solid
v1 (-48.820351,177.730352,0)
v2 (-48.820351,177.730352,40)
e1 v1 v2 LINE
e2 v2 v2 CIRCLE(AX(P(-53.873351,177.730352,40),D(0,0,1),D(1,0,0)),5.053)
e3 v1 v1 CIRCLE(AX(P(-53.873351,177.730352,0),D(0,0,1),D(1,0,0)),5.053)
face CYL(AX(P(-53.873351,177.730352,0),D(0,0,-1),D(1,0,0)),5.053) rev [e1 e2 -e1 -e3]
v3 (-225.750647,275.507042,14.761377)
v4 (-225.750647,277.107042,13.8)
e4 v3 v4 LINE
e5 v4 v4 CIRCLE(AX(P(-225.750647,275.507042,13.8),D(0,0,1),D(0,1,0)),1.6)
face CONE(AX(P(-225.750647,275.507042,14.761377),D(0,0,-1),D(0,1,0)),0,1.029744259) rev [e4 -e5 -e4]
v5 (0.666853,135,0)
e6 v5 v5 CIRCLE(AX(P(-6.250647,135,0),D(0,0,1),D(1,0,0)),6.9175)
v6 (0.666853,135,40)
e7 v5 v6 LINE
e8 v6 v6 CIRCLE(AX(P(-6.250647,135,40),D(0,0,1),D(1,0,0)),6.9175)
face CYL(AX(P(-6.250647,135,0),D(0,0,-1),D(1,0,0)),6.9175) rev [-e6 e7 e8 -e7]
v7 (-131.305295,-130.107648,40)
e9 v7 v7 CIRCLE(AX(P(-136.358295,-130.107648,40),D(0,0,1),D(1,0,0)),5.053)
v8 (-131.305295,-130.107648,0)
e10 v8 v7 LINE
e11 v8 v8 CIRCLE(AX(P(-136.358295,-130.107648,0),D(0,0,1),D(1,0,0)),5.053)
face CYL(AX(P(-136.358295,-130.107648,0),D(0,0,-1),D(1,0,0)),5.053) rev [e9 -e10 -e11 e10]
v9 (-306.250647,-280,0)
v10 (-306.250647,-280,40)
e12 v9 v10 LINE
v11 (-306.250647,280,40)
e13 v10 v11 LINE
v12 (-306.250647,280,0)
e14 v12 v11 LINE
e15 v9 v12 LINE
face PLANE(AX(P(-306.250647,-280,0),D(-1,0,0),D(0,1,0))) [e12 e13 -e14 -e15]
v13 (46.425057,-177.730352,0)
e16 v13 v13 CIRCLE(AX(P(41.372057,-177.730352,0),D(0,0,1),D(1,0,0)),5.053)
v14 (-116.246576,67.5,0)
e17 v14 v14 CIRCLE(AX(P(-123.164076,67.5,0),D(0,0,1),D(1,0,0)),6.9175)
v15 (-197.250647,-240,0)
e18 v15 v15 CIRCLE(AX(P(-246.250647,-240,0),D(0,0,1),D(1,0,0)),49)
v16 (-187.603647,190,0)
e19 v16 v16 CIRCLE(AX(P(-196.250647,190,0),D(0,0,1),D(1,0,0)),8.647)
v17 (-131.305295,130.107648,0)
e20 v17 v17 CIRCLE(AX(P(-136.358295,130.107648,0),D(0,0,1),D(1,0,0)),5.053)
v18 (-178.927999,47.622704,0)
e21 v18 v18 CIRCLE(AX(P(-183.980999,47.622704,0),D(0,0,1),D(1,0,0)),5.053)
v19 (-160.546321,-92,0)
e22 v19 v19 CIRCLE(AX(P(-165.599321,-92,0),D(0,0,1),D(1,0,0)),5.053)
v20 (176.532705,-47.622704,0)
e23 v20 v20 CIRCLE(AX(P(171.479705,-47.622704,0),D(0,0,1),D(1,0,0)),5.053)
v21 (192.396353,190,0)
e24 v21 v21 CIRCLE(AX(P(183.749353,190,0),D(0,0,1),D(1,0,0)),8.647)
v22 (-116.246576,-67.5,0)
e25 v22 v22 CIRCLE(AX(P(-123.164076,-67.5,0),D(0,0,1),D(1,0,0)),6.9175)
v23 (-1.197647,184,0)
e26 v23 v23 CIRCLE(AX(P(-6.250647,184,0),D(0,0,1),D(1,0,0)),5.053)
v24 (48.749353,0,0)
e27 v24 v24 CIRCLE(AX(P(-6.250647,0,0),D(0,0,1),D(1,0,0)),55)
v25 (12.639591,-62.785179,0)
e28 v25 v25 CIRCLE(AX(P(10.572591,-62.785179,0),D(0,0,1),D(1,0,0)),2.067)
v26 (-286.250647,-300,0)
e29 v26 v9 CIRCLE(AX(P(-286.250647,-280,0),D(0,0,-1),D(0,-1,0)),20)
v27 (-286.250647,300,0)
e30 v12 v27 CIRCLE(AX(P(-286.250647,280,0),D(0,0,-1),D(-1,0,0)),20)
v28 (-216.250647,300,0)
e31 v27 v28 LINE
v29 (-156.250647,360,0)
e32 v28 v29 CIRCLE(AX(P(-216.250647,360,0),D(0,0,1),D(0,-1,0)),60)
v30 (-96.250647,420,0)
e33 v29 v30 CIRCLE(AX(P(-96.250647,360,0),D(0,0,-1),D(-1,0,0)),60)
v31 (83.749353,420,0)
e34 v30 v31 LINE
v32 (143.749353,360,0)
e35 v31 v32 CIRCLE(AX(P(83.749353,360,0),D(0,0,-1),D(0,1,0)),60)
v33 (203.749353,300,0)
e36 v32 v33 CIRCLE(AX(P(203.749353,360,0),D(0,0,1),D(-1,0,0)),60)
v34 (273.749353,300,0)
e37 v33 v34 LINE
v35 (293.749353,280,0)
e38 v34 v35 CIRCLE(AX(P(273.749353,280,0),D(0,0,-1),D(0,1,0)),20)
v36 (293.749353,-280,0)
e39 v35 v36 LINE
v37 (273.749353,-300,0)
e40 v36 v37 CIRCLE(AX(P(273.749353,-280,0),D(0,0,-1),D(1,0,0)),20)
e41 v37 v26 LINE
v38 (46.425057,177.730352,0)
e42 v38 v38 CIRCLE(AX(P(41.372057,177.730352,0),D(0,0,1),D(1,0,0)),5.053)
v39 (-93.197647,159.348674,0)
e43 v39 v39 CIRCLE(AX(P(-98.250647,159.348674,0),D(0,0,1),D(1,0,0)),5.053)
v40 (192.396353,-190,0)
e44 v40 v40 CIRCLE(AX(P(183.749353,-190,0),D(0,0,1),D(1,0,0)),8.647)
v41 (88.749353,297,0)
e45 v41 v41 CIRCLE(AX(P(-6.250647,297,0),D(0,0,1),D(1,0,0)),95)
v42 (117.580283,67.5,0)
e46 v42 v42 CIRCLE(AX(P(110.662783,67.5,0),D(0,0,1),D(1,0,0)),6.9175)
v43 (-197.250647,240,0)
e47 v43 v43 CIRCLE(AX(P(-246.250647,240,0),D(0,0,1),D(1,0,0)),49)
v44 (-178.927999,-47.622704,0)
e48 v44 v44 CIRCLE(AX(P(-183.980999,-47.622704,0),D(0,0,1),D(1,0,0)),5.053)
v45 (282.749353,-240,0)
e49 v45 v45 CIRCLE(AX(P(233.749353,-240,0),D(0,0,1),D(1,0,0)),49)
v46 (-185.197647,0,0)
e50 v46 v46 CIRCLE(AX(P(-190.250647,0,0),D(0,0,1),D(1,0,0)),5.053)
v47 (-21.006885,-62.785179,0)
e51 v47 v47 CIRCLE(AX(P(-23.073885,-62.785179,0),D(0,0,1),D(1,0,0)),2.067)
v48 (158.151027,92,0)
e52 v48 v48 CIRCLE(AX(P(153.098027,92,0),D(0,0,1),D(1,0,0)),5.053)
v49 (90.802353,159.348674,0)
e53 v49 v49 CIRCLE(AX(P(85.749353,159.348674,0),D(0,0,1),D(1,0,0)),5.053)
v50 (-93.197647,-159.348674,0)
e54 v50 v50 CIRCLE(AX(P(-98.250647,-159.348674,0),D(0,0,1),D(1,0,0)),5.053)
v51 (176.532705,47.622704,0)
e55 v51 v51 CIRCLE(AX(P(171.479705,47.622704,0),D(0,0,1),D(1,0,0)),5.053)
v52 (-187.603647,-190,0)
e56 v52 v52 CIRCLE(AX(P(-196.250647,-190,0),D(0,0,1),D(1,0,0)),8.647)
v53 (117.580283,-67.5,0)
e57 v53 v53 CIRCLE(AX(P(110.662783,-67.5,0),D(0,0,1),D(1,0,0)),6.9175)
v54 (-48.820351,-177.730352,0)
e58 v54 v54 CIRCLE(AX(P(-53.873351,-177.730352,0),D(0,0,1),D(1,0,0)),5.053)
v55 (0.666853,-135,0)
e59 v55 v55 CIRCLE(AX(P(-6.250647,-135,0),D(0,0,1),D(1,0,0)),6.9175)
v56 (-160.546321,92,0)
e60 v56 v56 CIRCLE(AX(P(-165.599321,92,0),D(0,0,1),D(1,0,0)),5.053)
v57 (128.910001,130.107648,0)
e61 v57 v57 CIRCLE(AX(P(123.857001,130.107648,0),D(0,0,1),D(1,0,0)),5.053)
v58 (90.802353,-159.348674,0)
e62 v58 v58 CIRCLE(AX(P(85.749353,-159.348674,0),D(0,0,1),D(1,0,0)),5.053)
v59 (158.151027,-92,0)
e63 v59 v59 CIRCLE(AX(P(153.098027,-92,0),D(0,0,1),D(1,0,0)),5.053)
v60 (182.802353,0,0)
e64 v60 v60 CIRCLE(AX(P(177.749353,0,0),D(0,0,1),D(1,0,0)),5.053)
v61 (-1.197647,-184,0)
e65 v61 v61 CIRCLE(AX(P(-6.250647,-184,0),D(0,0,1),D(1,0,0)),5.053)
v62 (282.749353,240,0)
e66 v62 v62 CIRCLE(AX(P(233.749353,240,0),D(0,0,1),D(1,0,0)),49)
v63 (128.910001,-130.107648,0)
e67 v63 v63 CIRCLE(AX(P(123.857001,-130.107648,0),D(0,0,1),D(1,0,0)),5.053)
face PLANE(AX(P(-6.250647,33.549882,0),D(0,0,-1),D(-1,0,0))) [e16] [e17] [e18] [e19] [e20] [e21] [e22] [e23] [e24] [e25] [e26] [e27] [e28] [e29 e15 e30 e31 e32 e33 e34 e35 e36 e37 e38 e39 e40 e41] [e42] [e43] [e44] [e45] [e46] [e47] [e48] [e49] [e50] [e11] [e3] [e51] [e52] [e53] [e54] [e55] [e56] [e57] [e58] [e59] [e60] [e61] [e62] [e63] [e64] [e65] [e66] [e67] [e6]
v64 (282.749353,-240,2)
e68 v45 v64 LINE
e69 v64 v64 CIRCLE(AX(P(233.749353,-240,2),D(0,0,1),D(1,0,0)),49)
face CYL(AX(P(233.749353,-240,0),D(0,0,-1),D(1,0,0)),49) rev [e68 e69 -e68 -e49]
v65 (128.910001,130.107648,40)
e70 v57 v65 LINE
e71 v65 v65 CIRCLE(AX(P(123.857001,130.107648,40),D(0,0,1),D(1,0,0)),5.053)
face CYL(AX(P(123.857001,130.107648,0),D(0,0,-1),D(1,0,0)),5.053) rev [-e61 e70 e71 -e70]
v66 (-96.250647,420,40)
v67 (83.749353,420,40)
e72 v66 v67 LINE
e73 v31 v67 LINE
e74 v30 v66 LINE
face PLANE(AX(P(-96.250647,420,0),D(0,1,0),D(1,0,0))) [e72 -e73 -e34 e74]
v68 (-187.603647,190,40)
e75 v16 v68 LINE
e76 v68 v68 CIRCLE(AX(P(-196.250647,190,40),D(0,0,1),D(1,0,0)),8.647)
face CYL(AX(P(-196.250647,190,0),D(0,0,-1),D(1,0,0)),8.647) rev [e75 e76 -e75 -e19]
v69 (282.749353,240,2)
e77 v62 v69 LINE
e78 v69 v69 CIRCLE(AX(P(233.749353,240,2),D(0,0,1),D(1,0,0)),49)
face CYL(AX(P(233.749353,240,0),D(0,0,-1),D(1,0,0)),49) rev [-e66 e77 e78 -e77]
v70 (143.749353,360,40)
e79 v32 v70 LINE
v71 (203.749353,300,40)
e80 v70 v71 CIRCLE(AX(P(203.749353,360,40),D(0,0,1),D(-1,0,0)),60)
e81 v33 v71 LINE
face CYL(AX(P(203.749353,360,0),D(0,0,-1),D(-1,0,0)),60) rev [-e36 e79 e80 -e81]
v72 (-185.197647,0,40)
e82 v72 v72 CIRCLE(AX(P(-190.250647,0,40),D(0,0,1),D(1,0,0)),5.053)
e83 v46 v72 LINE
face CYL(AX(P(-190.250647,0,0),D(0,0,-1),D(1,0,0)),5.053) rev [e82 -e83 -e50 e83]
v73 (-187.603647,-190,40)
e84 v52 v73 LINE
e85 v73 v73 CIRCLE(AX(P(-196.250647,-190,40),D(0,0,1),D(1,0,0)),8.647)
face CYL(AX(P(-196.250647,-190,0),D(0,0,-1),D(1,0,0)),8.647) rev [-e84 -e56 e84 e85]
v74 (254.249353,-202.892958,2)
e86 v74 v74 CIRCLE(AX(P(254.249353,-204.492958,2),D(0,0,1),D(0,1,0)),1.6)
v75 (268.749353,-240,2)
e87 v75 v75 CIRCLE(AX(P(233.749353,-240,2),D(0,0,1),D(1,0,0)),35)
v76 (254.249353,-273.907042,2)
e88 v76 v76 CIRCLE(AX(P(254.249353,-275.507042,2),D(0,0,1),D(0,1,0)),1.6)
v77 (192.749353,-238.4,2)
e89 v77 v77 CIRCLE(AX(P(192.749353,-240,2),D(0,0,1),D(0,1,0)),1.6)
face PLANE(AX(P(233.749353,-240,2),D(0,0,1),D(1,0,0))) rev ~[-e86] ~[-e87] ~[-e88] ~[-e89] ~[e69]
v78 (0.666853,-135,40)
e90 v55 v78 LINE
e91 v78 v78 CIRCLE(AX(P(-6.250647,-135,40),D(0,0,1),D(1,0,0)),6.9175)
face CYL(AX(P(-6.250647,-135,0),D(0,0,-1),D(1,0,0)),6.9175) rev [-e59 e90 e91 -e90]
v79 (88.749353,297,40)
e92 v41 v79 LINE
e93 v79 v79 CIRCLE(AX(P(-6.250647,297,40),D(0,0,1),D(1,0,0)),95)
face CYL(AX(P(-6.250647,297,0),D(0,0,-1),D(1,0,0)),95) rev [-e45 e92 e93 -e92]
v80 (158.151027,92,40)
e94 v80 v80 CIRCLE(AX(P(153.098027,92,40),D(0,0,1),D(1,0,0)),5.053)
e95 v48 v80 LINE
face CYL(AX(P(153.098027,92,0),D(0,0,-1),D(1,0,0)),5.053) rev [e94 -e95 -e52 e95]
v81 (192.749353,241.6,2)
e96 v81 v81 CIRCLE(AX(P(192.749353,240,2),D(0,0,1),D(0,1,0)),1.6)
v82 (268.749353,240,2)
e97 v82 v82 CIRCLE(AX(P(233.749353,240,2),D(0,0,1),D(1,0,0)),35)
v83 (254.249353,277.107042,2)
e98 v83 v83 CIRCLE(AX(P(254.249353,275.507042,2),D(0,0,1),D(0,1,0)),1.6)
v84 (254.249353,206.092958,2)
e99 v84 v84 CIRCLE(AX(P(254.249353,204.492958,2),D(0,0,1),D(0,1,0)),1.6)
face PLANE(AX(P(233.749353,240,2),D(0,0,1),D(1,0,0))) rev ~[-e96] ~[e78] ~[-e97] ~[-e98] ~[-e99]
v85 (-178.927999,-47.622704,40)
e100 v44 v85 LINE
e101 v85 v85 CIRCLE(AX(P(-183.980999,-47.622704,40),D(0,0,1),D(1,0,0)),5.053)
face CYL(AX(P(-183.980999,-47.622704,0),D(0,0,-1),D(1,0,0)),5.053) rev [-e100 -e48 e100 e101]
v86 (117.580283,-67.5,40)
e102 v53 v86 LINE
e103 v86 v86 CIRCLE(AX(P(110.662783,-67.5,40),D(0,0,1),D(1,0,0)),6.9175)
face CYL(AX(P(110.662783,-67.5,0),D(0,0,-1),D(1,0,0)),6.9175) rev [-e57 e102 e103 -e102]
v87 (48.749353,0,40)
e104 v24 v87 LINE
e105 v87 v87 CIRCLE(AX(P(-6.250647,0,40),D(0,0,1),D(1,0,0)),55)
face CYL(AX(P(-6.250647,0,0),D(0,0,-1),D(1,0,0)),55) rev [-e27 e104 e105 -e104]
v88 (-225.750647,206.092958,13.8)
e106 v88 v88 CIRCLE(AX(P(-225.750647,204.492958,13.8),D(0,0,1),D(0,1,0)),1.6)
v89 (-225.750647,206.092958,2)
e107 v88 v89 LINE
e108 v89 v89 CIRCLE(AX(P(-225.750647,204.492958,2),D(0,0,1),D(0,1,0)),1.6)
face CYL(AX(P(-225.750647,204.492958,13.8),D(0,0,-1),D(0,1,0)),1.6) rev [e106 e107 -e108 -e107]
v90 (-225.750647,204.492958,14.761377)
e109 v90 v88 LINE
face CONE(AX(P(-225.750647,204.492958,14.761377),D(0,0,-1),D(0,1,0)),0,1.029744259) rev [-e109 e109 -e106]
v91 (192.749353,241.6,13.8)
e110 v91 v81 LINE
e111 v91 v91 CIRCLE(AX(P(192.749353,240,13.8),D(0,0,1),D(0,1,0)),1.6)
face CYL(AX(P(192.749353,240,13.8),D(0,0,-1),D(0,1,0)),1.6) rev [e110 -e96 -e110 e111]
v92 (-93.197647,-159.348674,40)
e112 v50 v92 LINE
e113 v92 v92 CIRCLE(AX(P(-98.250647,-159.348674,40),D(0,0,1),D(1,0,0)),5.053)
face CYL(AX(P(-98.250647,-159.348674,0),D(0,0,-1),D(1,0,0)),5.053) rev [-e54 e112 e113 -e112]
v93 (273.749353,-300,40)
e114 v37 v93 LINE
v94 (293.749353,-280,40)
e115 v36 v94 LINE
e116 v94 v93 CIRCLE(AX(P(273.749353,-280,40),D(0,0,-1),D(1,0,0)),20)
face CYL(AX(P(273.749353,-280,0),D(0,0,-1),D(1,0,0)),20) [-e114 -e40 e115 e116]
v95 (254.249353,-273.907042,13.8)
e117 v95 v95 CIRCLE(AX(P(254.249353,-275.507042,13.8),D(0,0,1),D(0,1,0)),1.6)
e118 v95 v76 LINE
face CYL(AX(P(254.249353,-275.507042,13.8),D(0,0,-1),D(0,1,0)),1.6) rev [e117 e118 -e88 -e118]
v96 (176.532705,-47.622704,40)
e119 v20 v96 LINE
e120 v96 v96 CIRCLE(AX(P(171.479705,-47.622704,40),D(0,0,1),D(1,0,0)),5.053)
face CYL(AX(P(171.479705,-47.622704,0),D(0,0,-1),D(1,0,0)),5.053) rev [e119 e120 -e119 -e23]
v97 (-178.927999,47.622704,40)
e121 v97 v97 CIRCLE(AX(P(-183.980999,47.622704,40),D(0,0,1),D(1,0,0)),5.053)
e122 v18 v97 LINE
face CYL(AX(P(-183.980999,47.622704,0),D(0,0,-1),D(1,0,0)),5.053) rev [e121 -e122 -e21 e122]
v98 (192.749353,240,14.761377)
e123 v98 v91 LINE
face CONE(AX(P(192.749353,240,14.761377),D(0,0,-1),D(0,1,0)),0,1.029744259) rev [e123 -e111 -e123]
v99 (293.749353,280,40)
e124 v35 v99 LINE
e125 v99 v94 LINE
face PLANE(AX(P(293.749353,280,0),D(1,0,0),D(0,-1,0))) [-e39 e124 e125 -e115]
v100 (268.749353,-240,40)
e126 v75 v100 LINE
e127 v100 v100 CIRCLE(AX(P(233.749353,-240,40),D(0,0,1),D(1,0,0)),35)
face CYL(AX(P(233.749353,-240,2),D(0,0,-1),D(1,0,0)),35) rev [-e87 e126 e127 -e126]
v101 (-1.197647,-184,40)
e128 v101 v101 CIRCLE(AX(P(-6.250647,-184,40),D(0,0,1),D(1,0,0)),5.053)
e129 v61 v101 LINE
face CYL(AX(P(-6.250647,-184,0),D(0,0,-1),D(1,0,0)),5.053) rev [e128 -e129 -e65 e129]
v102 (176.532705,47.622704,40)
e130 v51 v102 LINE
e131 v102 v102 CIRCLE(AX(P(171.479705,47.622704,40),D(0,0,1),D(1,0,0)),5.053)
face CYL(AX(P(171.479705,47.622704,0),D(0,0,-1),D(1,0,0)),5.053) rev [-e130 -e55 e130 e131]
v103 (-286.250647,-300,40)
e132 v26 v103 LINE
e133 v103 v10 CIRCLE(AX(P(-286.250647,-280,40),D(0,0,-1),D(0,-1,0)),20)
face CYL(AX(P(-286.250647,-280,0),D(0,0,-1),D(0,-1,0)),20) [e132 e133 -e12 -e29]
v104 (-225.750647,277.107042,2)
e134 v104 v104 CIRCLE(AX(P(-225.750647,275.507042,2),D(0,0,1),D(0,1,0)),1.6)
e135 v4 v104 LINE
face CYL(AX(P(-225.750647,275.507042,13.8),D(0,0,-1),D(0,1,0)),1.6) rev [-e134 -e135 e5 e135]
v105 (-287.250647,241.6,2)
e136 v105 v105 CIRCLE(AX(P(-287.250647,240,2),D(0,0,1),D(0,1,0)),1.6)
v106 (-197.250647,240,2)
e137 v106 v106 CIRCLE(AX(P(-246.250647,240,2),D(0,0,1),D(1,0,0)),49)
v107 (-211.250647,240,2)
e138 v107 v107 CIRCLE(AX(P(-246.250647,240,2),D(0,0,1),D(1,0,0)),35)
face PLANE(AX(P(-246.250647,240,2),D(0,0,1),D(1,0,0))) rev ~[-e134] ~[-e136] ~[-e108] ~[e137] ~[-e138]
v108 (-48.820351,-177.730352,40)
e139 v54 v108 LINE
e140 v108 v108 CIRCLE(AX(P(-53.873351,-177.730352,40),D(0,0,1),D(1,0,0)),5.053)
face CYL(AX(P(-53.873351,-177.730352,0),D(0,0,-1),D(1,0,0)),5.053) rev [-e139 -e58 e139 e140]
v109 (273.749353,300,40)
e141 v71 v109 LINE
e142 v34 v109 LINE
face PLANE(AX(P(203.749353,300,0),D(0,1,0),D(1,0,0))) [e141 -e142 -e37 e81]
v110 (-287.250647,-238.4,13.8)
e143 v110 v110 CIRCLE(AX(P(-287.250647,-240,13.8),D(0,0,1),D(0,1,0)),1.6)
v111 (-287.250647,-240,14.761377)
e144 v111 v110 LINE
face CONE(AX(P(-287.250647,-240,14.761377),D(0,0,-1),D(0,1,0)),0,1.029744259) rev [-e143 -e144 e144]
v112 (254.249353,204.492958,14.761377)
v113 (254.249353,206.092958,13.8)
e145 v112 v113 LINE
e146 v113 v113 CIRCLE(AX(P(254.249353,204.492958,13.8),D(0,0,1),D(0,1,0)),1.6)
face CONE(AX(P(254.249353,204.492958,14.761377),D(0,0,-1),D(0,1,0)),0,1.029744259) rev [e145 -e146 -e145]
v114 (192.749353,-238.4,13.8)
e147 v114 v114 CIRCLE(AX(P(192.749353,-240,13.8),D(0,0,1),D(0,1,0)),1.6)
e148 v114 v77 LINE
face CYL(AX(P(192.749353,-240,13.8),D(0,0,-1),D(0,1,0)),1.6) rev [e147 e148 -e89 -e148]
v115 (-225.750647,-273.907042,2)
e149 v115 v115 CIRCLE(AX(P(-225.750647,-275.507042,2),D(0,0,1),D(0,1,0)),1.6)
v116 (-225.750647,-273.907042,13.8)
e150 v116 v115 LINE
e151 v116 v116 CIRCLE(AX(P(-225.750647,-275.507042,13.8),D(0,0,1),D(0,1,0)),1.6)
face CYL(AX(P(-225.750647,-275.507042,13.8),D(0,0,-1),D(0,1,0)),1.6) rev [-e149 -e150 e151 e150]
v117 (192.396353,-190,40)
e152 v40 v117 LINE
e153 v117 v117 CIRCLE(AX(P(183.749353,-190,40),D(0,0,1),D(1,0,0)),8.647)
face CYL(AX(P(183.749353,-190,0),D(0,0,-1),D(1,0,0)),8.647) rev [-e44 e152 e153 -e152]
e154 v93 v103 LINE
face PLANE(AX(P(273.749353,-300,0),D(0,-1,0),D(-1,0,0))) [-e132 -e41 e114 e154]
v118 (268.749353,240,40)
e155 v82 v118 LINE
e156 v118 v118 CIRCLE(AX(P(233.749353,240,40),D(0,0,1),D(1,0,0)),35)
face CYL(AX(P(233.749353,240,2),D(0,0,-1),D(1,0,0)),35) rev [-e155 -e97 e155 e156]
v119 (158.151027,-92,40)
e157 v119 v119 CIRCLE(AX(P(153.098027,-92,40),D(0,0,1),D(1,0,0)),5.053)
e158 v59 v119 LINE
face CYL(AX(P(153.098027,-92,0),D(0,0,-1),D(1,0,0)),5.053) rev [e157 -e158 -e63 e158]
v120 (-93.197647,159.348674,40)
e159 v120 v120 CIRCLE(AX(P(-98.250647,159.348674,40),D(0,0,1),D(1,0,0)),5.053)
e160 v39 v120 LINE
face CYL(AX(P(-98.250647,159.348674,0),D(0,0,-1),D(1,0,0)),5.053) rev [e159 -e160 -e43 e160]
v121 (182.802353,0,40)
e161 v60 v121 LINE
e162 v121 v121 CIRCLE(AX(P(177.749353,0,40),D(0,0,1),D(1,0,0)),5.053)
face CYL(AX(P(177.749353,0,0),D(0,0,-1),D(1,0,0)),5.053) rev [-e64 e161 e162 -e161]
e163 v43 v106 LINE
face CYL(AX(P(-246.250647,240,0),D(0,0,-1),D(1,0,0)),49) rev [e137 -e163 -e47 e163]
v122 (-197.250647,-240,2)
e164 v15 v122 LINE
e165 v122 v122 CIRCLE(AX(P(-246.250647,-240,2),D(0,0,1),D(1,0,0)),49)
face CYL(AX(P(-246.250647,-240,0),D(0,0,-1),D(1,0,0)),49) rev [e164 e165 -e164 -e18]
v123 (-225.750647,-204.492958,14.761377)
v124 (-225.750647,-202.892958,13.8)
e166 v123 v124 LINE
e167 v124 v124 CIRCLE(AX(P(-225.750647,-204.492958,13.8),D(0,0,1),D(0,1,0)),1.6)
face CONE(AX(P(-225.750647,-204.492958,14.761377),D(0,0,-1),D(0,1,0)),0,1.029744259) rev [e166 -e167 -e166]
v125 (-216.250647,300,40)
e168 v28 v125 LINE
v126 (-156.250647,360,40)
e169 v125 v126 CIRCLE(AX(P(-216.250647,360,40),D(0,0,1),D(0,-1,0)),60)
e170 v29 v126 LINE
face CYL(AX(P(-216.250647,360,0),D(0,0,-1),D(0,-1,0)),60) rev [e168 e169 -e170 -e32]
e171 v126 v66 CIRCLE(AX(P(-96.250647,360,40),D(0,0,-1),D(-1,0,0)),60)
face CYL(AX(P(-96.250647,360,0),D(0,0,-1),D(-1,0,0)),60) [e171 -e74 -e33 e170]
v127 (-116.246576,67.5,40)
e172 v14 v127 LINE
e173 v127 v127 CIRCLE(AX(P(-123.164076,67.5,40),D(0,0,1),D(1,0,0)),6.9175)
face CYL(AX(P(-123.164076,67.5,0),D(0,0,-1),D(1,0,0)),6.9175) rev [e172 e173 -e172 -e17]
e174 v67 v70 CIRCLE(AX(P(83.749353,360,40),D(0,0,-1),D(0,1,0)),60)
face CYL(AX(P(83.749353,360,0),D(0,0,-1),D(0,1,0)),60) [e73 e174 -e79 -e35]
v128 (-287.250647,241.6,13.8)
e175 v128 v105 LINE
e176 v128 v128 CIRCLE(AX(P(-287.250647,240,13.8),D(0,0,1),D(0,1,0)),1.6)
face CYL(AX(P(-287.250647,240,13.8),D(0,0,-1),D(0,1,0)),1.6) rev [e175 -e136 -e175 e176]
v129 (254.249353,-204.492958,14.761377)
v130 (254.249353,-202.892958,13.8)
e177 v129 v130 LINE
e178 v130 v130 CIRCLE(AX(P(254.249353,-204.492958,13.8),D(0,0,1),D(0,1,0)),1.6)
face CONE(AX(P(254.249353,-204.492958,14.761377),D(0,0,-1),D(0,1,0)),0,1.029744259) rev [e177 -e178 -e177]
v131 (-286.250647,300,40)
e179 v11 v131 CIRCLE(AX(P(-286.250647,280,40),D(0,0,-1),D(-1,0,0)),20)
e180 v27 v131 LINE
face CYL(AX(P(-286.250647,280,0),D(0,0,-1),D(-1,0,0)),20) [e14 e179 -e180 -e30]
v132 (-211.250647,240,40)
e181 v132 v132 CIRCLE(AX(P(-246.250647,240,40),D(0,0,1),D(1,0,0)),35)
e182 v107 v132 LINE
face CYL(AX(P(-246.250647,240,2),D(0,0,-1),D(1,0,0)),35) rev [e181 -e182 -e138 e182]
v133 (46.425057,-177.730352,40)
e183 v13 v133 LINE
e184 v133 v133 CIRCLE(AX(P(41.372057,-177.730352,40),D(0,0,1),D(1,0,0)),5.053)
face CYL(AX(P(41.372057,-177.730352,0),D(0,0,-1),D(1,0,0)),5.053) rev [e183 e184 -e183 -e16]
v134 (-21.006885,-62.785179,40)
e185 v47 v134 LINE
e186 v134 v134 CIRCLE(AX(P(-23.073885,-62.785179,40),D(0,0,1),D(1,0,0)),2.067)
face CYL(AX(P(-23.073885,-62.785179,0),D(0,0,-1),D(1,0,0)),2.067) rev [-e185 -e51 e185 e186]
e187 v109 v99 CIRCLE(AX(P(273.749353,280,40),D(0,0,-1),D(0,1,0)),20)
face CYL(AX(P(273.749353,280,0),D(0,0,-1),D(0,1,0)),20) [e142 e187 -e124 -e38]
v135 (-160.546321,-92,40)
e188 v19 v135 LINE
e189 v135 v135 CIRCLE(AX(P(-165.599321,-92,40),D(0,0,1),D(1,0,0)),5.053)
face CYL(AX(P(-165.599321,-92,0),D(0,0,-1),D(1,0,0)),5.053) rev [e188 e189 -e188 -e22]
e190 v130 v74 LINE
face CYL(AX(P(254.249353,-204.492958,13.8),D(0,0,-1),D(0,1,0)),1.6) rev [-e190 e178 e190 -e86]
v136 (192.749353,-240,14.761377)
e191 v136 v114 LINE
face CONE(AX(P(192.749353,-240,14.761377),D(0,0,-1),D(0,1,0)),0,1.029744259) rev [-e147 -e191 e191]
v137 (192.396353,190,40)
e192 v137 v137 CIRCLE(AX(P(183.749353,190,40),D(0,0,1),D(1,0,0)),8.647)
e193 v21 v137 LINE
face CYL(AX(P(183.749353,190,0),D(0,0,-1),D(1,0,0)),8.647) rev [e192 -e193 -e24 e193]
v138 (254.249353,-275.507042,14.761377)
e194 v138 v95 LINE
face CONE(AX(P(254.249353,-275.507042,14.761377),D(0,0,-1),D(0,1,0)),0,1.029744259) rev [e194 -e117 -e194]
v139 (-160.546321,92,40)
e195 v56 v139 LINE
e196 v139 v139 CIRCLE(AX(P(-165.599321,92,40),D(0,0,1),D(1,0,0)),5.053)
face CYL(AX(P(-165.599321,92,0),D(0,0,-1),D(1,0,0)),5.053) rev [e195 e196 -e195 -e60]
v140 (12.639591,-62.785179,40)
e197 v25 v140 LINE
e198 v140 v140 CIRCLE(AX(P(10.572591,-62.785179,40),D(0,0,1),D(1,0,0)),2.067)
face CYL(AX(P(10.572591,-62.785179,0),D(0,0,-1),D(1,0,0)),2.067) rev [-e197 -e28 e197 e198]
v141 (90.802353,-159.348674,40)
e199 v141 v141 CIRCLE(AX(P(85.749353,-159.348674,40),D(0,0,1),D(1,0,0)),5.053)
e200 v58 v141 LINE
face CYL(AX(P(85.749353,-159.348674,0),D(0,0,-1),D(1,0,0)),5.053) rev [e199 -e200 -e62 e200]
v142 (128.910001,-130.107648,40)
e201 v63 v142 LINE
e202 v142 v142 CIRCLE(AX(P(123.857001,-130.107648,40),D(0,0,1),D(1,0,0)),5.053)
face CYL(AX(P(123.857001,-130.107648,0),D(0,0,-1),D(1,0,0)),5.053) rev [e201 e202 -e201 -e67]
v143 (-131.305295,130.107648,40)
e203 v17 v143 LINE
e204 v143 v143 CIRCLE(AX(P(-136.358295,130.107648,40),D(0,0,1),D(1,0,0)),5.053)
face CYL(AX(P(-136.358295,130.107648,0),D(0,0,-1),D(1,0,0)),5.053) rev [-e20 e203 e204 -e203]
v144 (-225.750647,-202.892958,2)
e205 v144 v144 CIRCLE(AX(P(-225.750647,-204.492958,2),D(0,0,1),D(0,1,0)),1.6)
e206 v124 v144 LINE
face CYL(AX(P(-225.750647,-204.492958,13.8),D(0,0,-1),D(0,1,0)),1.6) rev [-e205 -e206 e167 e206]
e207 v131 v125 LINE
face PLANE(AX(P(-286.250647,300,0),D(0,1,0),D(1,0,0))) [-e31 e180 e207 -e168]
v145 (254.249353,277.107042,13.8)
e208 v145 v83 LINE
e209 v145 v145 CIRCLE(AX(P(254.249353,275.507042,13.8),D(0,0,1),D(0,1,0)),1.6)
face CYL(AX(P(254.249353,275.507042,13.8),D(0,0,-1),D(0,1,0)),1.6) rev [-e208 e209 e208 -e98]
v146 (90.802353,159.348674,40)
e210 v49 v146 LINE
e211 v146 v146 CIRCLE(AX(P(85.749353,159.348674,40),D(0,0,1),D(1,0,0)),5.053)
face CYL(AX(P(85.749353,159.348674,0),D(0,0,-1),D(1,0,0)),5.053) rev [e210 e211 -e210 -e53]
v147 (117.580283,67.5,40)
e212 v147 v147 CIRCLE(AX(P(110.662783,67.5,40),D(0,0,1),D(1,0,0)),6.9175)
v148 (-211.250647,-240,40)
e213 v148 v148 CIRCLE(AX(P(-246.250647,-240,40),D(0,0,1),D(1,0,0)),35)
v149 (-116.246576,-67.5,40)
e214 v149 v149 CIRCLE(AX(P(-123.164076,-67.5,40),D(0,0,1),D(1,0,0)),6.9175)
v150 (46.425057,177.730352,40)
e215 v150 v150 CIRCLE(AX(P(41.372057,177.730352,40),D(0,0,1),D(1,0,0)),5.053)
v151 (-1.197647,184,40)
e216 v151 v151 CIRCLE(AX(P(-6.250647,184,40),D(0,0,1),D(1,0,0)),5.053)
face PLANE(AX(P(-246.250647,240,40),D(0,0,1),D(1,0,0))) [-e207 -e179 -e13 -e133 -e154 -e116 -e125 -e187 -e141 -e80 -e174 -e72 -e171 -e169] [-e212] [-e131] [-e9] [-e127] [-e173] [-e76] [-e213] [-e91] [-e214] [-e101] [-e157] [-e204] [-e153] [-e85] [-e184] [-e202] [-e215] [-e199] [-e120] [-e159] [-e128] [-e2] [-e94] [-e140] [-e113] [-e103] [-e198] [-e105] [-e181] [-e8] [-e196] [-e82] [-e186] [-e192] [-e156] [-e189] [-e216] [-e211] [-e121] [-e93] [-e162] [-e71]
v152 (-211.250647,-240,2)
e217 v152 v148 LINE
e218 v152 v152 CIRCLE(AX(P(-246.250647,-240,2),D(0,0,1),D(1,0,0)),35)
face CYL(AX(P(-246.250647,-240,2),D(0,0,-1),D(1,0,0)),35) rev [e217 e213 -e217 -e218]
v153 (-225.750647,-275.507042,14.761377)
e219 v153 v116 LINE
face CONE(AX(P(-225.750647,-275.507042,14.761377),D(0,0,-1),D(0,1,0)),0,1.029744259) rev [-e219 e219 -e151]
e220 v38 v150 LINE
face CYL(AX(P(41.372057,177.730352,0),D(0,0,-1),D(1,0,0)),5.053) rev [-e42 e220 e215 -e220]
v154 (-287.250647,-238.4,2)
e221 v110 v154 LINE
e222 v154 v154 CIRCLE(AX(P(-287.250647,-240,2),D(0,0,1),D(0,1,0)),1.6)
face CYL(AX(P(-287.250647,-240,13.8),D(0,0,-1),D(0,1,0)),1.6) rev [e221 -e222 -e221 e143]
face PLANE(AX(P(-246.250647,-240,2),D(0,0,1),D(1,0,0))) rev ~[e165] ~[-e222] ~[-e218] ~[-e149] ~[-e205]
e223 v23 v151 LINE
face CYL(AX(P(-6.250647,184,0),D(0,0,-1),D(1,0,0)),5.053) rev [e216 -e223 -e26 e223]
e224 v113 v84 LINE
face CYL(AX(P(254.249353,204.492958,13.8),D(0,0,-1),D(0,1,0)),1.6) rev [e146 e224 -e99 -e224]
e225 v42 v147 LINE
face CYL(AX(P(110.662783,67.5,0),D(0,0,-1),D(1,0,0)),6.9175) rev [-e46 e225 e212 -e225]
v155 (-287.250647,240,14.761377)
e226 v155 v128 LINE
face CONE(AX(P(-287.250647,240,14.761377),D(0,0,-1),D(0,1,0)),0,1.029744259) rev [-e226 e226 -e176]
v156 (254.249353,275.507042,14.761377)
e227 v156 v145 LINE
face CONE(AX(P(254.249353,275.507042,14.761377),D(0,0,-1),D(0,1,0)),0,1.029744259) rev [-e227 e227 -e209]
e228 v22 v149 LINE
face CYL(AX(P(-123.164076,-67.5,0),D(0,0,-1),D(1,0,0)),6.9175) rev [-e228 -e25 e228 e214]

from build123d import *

# Parameters (mm, degrees)
SKETCH1_R                       = 49
SKETCH1_R_2                     = 55
SKETCH1_R_3                     = 5.053
SKETCH1_R_4                     = 95
SKETCH1_R_5                     = 6.9175
SKETCH1_R_6                     = 8.647
SKETCH1_R_7                     = 2.067
BOSS_EXTRUDE1_DEPTH             = 40
BOSS_EXTRUDE2_START             = -38
SKETCH2_R                       = 49
SKETCH2_R_2                     = 35
BOSS_EXTRUDE2_DEPTH             = 38
SIZE_MM_DOWEL_HOLE_1_AT_2_COUNT = 2
SIZE_MM_DOWEL_HOLE_1_AT_2_PITCH = 71.01408311
SIZE_MM_DOWEL_HOLE_1_AT_3_COUNT = 2
SIZE_MM_DOWEL_HOLE_1_AT_3_PITCH = 71.01408311
LPATTERN1_COUNT                 = 2
LPATTERN1_PITCH                 = 480
LPATTERN1_COUNT_DIR2            = 2
LPATTERN1_PITCH_DIR2            = 480


with BuildPart() as part:
    # Sketch1 → Boss-Extrude1 (new body)
    with BuildSketch(Plane.XY):
        with BuildLine():
            Line((-96.250646967, 420), (83.749353033, 420))
            ThreePointArc((83.749353033, 420), (126.175759905, 402.426406871), (143.749353033, 360))
            ThreePointArc((143.749353033, 360), (161.322946162, 317.573593129), (203.749353033, 300))
            Line((203.749353033, 300), (273.749353033, 300))
            ThreePointArc((273.749353033, 300), (287.891488657, 294.142135624), (293.749353033, 280))
            Line((293.749353033, 280), (293.749353033, -280))
            ThreePointArc((293.749353033, -280), (287.891488657, -294.142135624), (273.749353033, -300))
            Line((273.749353033, -300), (-286.250646967, -300))
            ThreePointArc((-286.250646967, -300), (-300.39278259, -294.142135624), (-306.250646967, -280))
            Line((-306.250646967, -280), (-306.250646967, 280))
            ThreePointArc((-306.250646967, 280), (-300.39278259, 294.142135624), (-286.250646967, 300))
            Line((-286.250646967, 300), (-216.250646967, 300))
            ThreePointArc((-216.250646967, 300), (-173.824240095, 317.573593129), (-156.250646967, 360))
            ThreePointArc((-156.250646967, 360), (-138.677053838, 402.426406871), (-96.250646967, 420))
        make_face()
        with Locations((-246.250646967, 240)):
            Circle(SKETCH1_R, mode=Mode.SUBTRACT)
        with Locations((233.749353033, -240)):
            Circle(SKETCH1_R, mode=Mode.SUBTRACT)
        with Locations((-246.250646967, -240)):
            Circle(SKETCH1_R, mode=Mode.SUBTRACT)
        with Locations((233.749353033, 240)):
            Circle(SKETCH1_R, mode=Mode.SUBTRACT)
        with Locations((-6.250646967, 0)):
            Circle(SKETCH1_R_2, mode=Mode.SUBTRACT)
        with Locations((-6.250646967, -184)):
            Circle(SKETCH1_R_3, mode=Mode.SUBTRACT)
        with Locations((-53.873351265, -177.730352037)):
            Circle(SKETCH1_R_3, mode=Mode.SUBTRACT)
        with Locations((-98.250646967, -159.348674296)):
            Circle(SKETCH1_R_3, mode=Mode.SUBTRACT)
        with Locations((-136.358294705, -130.107647738)):
            Circle(SKETCH1_R_3, mode=Mode.SUBTRACT)
        with Locations((-165.599321263, -92)):
            Circle(SKETCH1_R_3, mode=Mode.SUBTRACT)
        with Locations((-183.980999004, -47.622704299)):
            Circle(SKETCH1_R_3, mode=Mode.SUBTRACT)
        with Locations((-190.250646967, 0)):
            Circle(SKETCH1_R_3, mode=Mode.SUBTRACT)
        with Locations((-183.980999004, 47.622704299)):
            Circle(SKETCH1_R_3, mode=Mode.SUBTRACT)
        with Locations((-165.599321263, 92)):
            Circle(SKETCH1_R_3, mode=Mode.SUBTRACT)
        with Locations((-136.358294705, 130.107647738)):
            Circle(SKETCH1_R_3, mode=Mode.SUBTRACT)
        with Locations((-98.250646967, 159.348674296)):
            Circle(SKETCH1_R_3, mode=Mode.SUBTRACT)
        with Locations((-53.873351265, 177.730352037)):
            Circle(SKETCH1_R_3, mode=Mode.SUBTRACT)
        with Locations((-6.250646967, 184)):
            Circle(SKETCH1_R_3, mode=Mode.SUBTRACT)
        with Locations((41.372057332, 177.730352037)):
            Circle(SKETCH1_R_3, mode=Mode.SUBTRACT)
        with Locations((85.749353033, 159.348674296)):
            Circle(SKETCH1_R_3, mode=Mode.SUBTRACT)
        with Locations((123.857000772, 130.107647738)):
            Circle(SKETCH1_R_3, mode=Mode.SUBTRACT)
        with Locations((153.09802733, 92)):
            Circle(SKETCH1_R_3, mode=Mode.SUBTRACT)
        with Locations((171.479705071, 47.622704299)):
            Circle(SKETCH1_R_3, mode=Mode.SUBTRACT)
        with Locations((177.749353033, 0)):
            Circle(SKETCH1_R_3, mode=Mode.SUBTRACT)
        with Locations((171.479705071, -47.622704299)):
            Circle(SKETCH1_R_3, mode=Mode.SUBTRACT)
        with Locations((153.09802733, -92)):
            Circle(SKETCH1_R_3, mode=Mode.SUBTRACT)
        with Locations((123.857000772, -130.107647738)):
            Circle(SKETCH1_R_3, mode=Mode.SUBTRACT)
        with Locations((85.749353033, -159.348674296)):
            Circle(SKETCH1_R_3, mode=Mode.SUBTRACT)
        with Locations((41.372057332, -177.730352037)):
            Circle(SKETCH1_R_3, mode=Mode.SUBTRACT)
        with Locations((-6.250646967, 297)):
            Circle(SKETCH1_R_4, mode=Mode.SUBTRACT)
        with Locations((-6.250646967, 135)):
            Circle(SKETCH1_R_5, mode=Mode.SUBTRACT)
        with Locations((110.662782544, 67.5)):
            Circle(SKETCH1_R_5, mode=Mode.SUBTRACT)
        with Locations((110.662782544, -67.5)):
            Circle(SKETCH1_R_5, mode=Mode.SUBTRACT)
        with Locations((-6.250646967, -135)):
            Circle(SKETCH1_R_5, mode=Mode.SUBTRACT)
        with Locations((-123.164076477, -67.5)):
            Circle(SKETCH1_R_5, mode=Mode.SUBTRACT)
        with Locations((-123.164076477, 67.5)):
            Circle(SKETCH1_R_5, mode=Mode.SUBTRACT)
        with Locations((-196.250646967, 190)):
            Circle(SKETCH1_R_6, mode=Mode.SUBTRACT)
        with Locations((183.749353033, -190)):
            Circle(SKETCH1_R_6, mode=Mode.SUBTRACT)
        with Locations((-196.250646967, -190)):
            Circle(SKETCH1_R_6, mode=Mode.SUBTRACT)
        with Locations((183.749353033, 190)):
            Circle(SKETCH1_R_6, mode=Mode.SUBTRACT)
        with Locations((-23.073884898, -62.785178709)):
            Circle(SKETCH1_R_7, mode=Mode.SUBTRACT)
        with Locations((10.572590965, -62.785178709)):
            Circle(SKETCH1_R_7, mode=Mode.SUBTRACT)
    extrude(amount=BOSS_EXTRUDE1_DEPTH)

    # Sketch2 → Boss-Extrude2 (add)
    # profile 1 of 4: a face of its own
    with BuildSketch(Plane.XY.offset(40).offset(BOSS_EXTRUDE2_START)):
        with Locations((-246.250646967, 240)):
            Circle(SKETCH2_R)
        with Locations((-246.250646967, 240)):
            Circle(SKETCH2_R_2, mode=Mode.SUBTRACT)
    # profile 2 of 4: a face of its own
    with BuildSketch(Plane.XY.offset(40).offset(BOSS_EXTRUDE2_START)):
        with Locations((233.749353033, 240)):
            Circle(SKETCH2_R)
        with Locations((233.749353033, 240)):
            Circle(SKETCH2_R_2, mode=Mode.SUBTRACT)
    # profile 3 of 4: a face of its own
    with BuildSketch(Plane.XY.offset(40).offset(BOSS_EXTRUDE2_START)):
        with Locations((233.749353033, -240)):
            Circle(SKETCH2_R)
        with Locations((233.749353033, -240)):
            Circle(SKETCH2_R_2, mode=Mode.SUBTRACT)
    # profile 4 of 4: a face of its own
    with BuildSketch(Plane.XY.offset(40).offset(BOSS_EXTRUDE2_START)):
        with Locations((-246.250646967, -240)):
            Circle(SKETCH2_R)
        with Locations((-246.250646967, -240)):
            Circle(SKETCH2_R_2, mode=Mode.SUBTRACT)
    extrude(amount=BOSS_EXTRUDE2_DEPTH)

    # Sketch5 → Size mm Dowel hole 1 (revolve, cut)
    with BuildSketch(Plane(origin=(254.249353033, 275.507041555, 2), x_dir=(0, 1, 0), z_dir=(1, 0, 0))):
        Polygon((0, 0), (0, 12.76137699), (1.6, 11.8), (1.6, 0), align=None)
    size_mm_dowel_hole_1 = revolve(axis=Axis((254.249353033, 275.507041555, -4.35), (0, 0, 1)), mode=Mode.SUBTRACT)

    # Size mm Dowel hole 1 at 2: Size mm Dowel hole 1 ×2
    with Locations(*[Vector(-0.8660254037844366, -0.5000000000000037, 0) * (i * SIZE_MM_DOWEL_HOLE_1_AT_2_PITCH) for i in range(1, SIZE_MM_DOWEL_HOLE_1_AT_2_COUNT)]):
        add(size_mm_dowel_hole_1, mode=Mode.SUBTRACT)

    # Size mm Dowel hole 1 at 3: Size mm Dowel hole 1 ×2
    with Locations(*[(0, -i * SIZE_MM_DOWEL_HOLE_1_AT_3_PITCH, 0) for i in range(1, SIZE_MM_DOWEL_HOLE_1_AT_3_COUNT)]):
        add(size_mm_dowel_hole_1, mode=Mode.SUBTRACT)

    # LPattern1: Size mm Dowel hole 1 2 × 2
    with Locations(*[(-i * LPATTERN1_PITCH, -j * LPATTERN1_PITCH_DIR2, 0) for i in range(LPATTERN1_COUNT) for j in range(LPATTERN1_COUNT_DIR2) if (i, j) != (0, 0)]):
        add(size_mm_dowel_hole_1, mode=Mode.SUBTRACT)

    # LPattern1 copy 1 sketch → LPattern1 copy 1 (revolve, cut)
    with BuildSketch(Plane(origin=(192.749353033, -240, 2), x_dir=(0, 1, 0), z_dir=(1, 0, 0))):
        Polygon((0, 0), (0, 12.76137699), (1.6, 11.8), (1.6, 0), align=None)
    revolve(axis=Axis((192.749353033, -240, -4.35), (0, 0, 1)), mode=Mode.SUBTRACT)

    # LPattern1 copy 2 sketch → LPattern1 copy 2 (revolve, cut)
    with BuildSketch(Plane(origin=(-287.250646967, 240, 2), x_dir=(0, 1, 0), z_dir=(1, 0, 0))):
        Polygon((0, 0), (0, 12.76137699), (1.6, 11.8), (1.6, 0), align=None)
    revolve(axis=Axis((-287.250646967, 240, -4.35), (0, 0, 1)), mode=Mode.SUBTRACT)

    # LPattern1 copy 3 sketch → LPattern1 copy 3 (revolve, cut)
    with BuildSketch(Plane(origin=(-287.250646967, -240, 2), x_dir=(0, 1, 0), z_dir=(1, 0, 0))):
        Polygon((0, 0), (0, 12.76137699), (1.6, 11.8), (1.6, 0), align=None)
    revolve(axis=Axis((-287.250646967, -240, -4.35), (0, 0, 1)), mode=Mode.SUBTRACT)

    # LPattern1 copy 4 sketch → LPattern1 copy 4 (revolve, cut)
    with BuildSketch(Plane(origin=(254.249353033, -275.507041555, 2), x_dir=(0, 1, 0), z_dir=(1, 0, 0))):
        Polygon((0, 0), (0, 12.76137699), (1.6, 11.8), (1.6, 0), align=None)
    revolve(axis=Axis((254.249353033, -275.507041555, -4.35), (0, 0, 1)), mode=Mode.SUBTRACT)

    # LPattern1 copy 5 sketch → LPattern1 copy 5 (revolve, cut)
    with BuildSketch(Plane(origin=(-225.750646967, 204.492958445, 2), x_dir=(0, 1, 0), z_dir=(1, 0, 0))):
        Polygon((0, 0), (0, 12.76137699), (1.6, 11.8), (1.6, 0), align=None)
    revolve(axis=Axis((-225.750646967, 204.492958445, -4.35), (0, 0, 1)), mode=Mode.SUBTRACT)

    # LPattern1 copy 6 sketch → LPattern1 copy 6 (revolve, cut)
    with BuildSketch(Plane(origin=(-225.750646967, -275.507041555, 2), x_dir=(0, 1, 0), z_dir=(1, 0, 0))):
        Polygon((0, 0), (0, 12.76137699), (1.6, 11.8), (1.6, 0), align=None)
    revolve(axis=Axis((-225.750646967, -275.507041555, -4.35), (0, 0, 1)), mode=Mode.SUBTRACT)


solid = part.part
